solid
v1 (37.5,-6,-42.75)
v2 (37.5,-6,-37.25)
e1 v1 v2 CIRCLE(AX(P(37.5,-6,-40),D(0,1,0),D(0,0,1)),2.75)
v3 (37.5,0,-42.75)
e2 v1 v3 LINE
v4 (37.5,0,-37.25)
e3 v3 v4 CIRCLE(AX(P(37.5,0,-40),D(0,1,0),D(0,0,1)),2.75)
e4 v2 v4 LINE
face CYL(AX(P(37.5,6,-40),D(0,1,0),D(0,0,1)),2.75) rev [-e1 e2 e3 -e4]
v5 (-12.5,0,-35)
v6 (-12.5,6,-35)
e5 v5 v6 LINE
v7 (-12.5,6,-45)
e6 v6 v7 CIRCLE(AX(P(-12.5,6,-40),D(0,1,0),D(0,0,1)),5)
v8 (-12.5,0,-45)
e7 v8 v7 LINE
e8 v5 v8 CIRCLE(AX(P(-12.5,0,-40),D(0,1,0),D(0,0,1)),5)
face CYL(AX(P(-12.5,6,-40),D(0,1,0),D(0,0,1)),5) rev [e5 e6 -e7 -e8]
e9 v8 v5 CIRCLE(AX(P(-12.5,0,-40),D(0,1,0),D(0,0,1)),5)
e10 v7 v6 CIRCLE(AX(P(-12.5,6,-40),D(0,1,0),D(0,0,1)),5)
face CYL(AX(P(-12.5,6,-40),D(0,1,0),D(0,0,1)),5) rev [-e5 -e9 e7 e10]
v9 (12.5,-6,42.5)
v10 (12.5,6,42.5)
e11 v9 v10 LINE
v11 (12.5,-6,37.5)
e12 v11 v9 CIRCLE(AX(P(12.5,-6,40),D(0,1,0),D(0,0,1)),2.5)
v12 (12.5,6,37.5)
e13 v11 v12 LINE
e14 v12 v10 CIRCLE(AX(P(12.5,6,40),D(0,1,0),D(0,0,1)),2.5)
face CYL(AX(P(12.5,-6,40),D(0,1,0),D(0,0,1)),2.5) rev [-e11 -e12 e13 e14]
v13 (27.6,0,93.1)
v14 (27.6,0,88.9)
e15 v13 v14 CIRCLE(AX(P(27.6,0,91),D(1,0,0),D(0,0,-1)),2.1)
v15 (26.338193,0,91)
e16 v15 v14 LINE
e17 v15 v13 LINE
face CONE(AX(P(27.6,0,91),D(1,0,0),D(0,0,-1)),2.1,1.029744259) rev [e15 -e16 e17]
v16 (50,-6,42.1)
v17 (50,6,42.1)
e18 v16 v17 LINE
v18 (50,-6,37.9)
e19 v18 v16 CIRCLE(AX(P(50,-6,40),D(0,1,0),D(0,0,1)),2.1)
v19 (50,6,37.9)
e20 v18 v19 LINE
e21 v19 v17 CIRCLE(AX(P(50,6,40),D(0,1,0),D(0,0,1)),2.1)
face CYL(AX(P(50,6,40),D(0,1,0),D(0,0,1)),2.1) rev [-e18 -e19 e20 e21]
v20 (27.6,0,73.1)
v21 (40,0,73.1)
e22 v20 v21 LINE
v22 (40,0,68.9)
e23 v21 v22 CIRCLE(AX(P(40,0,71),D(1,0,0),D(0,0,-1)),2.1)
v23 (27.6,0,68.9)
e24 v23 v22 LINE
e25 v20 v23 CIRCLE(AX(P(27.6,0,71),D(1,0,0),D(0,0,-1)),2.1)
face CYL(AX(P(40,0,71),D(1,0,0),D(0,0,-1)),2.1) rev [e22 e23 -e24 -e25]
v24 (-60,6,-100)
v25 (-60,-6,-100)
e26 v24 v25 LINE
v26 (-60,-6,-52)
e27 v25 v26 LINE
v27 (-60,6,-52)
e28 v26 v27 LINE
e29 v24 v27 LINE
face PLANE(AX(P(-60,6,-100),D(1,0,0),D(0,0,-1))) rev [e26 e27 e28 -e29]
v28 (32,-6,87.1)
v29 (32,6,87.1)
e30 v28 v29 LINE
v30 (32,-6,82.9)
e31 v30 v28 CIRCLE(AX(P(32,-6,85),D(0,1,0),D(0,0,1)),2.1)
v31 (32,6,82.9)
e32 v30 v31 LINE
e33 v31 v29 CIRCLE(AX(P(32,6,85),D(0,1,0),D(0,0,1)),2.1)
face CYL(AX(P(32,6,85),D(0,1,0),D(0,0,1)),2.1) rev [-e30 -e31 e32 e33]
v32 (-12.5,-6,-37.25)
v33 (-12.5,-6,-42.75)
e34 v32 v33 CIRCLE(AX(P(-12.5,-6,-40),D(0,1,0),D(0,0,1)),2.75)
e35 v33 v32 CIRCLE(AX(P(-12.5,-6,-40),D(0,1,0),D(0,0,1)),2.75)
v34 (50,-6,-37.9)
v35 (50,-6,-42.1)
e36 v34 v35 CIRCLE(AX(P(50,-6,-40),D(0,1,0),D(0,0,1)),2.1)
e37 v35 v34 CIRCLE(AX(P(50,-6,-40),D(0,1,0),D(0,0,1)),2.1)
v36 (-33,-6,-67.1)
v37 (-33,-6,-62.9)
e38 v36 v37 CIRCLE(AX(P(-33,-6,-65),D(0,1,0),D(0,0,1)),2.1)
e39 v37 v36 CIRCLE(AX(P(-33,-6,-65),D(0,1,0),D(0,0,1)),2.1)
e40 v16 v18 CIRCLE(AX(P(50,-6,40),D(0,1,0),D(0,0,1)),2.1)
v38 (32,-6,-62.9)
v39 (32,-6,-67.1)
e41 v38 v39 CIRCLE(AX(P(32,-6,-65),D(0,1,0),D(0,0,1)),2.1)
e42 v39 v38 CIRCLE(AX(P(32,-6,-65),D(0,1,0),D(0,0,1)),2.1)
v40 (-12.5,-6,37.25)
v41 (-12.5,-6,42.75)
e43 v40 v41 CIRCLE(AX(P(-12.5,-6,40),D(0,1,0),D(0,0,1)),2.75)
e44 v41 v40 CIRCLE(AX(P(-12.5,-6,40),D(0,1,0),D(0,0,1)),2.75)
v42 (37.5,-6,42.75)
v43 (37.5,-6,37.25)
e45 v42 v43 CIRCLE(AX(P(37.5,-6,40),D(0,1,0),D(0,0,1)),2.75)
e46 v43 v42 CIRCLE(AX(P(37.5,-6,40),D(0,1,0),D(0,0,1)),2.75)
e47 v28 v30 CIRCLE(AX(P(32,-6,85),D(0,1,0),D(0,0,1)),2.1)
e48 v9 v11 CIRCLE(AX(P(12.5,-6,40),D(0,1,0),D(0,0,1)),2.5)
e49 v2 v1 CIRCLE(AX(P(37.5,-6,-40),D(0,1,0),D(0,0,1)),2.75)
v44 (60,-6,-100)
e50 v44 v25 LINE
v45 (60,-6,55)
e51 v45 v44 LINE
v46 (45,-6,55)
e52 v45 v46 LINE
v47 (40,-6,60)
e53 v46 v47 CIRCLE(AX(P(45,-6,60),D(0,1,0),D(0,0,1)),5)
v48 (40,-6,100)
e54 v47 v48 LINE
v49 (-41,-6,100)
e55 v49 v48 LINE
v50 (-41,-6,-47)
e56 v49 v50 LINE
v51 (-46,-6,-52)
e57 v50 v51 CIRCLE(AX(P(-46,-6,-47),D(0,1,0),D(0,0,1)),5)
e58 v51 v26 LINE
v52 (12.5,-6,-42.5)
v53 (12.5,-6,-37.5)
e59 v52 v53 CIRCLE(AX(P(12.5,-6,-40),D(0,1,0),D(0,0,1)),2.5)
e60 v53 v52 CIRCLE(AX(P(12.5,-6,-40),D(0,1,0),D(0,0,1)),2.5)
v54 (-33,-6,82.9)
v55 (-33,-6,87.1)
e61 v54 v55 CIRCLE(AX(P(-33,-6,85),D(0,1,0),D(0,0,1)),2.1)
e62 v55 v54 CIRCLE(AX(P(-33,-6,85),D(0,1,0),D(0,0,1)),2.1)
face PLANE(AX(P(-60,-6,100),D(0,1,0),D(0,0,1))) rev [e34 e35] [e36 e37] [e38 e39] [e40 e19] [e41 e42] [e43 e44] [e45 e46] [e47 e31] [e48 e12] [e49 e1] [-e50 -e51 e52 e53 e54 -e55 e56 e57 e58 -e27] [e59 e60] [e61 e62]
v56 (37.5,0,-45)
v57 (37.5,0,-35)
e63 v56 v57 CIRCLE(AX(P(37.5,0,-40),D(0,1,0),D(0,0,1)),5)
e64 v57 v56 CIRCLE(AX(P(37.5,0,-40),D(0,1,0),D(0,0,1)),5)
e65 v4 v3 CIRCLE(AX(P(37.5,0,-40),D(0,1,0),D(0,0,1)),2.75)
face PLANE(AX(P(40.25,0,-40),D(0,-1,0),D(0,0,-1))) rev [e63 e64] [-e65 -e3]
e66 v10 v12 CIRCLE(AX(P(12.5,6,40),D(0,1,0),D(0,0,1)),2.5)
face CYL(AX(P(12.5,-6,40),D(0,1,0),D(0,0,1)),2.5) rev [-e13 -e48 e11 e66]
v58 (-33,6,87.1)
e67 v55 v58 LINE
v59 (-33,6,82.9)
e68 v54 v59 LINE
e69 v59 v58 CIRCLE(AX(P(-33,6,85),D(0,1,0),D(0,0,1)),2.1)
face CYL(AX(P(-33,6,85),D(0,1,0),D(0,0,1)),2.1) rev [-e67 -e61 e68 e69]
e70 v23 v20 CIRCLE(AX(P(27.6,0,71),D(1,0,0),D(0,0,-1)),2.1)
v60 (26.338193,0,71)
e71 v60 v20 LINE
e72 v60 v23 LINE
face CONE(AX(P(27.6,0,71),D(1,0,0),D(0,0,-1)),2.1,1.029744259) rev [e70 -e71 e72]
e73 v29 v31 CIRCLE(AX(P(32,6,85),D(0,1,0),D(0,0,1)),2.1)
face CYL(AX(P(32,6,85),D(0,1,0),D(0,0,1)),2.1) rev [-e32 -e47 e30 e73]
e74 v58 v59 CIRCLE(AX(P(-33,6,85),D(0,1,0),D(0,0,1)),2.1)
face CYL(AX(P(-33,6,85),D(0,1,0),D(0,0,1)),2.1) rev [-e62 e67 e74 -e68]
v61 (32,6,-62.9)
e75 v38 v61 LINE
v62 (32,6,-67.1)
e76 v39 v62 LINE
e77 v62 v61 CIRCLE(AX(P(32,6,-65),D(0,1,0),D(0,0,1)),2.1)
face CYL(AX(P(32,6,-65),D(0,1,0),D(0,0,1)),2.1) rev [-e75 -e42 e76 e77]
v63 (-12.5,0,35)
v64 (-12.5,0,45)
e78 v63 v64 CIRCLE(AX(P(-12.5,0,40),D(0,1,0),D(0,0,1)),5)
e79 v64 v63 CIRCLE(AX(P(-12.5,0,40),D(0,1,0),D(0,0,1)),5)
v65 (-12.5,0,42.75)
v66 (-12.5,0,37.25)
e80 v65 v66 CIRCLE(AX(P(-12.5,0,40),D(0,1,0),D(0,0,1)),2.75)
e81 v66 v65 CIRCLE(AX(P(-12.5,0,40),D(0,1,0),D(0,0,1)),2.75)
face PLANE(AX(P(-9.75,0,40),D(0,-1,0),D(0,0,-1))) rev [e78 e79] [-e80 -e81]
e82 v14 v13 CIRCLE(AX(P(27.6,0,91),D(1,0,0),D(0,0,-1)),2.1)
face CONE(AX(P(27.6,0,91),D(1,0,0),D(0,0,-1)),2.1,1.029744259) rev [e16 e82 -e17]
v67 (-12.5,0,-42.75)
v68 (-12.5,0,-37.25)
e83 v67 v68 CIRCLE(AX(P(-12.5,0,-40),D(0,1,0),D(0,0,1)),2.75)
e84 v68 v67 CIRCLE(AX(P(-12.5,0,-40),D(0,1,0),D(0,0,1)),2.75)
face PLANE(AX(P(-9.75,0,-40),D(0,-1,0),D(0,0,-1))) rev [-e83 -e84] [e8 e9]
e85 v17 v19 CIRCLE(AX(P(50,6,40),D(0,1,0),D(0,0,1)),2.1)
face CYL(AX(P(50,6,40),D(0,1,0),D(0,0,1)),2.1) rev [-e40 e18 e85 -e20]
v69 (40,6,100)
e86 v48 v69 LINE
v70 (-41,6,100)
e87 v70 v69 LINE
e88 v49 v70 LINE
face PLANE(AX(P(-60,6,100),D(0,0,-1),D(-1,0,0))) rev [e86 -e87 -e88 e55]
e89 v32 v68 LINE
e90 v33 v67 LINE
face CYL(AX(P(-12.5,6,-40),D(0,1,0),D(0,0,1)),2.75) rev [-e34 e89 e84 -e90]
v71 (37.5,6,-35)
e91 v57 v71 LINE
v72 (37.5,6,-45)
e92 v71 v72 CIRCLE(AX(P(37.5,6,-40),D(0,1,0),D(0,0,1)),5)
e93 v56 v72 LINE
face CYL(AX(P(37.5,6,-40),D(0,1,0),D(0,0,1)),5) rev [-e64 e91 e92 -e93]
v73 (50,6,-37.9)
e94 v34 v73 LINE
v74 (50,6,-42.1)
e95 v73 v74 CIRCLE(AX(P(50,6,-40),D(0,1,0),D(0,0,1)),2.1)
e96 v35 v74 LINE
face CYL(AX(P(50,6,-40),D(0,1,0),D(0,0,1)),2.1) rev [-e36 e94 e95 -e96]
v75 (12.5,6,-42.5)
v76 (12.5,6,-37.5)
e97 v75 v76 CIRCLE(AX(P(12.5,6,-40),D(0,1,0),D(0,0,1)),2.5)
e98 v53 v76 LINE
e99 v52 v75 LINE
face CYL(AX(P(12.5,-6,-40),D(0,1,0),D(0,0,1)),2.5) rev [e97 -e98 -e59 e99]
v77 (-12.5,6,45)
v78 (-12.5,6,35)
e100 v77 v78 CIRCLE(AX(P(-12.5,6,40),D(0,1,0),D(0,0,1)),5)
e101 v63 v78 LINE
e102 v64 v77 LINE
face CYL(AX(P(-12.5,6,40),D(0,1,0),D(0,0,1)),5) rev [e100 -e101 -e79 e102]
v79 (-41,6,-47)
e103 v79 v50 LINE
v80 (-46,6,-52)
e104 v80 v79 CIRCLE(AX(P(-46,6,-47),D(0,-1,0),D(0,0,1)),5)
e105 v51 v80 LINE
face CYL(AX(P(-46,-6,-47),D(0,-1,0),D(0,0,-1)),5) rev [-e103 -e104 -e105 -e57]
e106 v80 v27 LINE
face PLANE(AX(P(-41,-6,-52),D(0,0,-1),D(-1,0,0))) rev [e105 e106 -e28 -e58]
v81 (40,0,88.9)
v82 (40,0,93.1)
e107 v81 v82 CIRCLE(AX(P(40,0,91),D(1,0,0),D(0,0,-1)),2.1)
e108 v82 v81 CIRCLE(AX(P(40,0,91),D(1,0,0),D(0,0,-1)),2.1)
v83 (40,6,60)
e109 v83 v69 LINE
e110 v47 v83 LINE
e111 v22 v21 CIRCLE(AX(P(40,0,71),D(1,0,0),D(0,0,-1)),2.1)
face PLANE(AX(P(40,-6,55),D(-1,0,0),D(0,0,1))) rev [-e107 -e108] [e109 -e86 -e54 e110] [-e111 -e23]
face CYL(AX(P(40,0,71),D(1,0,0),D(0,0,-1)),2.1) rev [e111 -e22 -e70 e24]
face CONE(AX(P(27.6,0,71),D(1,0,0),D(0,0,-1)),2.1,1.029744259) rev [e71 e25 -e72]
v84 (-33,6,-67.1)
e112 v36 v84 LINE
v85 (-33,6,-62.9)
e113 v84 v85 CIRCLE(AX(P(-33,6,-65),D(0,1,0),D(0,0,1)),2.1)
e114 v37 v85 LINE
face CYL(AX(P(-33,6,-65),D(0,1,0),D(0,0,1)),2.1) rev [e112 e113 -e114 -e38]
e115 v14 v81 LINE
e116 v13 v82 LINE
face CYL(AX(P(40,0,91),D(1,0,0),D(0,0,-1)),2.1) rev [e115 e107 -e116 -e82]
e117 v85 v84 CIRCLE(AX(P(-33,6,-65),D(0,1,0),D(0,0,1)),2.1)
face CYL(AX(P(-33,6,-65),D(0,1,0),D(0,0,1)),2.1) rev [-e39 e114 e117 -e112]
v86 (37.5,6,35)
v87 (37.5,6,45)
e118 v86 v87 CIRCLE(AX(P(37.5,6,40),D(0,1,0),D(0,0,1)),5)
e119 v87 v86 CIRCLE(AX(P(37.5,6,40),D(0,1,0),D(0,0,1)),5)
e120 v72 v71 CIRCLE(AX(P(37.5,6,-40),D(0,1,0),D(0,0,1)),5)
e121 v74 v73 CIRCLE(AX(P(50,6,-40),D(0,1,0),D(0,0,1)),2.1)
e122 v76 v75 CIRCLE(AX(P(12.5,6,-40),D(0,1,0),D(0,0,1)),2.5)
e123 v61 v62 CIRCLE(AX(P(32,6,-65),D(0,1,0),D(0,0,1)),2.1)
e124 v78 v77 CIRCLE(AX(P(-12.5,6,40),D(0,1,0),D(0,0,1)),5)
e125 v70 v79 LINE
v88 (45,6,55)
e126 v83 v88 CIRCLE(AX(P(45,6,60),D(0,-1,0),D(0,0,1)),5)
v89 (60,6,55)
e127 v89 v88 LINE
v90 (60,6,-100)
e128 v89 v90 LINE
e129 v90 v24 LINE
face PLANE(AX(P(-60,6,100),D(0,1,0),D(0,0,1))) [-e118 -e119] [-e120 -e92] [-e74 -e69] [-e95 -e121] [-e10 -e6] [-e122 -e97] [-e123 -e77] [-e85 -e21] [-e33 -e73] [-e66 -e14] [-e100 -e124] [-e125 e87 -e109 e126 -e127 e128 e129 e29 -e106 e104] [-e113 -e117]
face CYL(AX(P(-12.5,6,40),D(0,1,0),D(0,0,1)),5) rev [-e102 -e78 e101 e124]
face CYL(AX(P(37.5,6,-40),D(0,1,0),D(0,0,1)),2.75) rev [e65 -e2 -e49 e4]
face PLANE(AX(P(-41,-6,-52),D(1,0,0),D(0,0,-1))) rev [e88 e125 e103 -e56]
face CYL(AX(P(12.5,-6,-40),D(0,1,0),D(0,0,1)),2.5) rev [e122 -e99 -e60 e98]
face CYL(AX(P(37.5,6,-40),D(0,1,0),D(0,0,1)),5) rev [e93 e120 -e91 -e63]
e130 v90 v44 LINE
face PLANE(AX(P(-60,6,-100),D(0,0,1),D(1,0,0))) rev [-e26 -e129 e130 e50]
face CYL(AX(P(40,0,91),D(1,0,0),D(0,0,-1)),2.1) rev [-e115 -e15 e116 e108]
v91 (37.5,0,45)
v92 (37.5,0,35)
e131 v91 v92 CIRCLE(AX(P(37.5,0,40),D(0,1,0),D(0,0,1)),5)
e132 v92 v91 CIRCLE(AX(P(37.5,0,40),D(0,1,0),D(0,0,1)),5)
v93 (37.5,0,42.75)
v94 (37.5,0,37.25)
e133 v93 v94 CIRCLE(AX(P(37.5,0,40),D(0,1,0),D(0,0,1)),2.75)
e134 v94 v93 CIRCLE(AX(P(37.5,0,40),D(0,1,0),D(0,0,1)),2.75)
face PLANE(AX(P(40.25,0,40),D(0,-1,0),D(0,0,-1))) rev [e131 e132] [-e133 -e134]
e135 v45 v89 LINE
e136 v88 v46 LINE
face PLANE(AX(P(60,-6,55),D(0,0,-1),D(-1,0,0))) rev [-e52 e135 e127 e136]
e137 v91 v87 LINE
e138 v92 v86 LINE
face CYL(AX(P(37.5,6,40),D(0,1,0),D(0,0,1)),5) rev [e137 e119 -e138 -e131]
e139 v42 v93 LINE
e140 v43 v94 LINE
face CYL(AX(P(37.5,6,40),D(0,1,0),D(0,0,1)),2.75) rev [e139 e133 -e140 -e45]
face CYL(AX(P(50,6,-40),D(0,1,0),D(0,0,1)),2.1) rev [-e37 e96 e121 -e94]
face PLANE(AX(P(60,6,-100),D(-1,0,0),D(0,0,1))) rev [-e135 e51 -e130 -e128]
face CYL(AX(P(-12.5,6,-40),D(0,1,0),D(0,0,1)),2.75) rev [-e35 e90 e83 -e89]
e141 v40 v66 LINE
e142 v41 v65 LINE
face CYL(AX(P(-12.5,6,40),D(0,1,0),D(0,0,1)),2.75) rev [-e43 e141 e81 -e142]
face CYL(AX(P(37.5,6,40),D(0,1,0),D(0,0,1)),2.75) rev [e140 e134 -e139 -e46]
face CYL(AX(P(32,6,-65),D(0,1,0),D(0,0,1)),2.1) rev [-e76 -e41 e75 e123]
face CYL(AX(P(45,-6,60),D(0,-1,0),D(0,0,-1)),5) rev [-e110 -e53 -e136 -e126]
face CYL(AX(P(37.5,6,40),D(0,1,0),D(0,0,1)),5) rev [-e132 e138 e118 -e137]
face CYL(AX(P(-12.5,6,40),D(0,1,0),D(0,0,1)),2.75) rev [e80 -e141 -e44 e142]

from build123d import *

# Parameters (mm, degrees)
SKETCH1_W                                         = 120
SKETCH1_H                                         = 200
EXTRUDE1_DEPTH                                    = 6
SKETCH3_W                                         = 19
SKETCH3_H                                         = 152
CUT_EXTRUDE1_DEPTH                                = 118.234807118
FILLET1_R                                         = 5
SKETCH4_W                                         = 20
SKETCH4_H                                         = 45
CUT_EXTRUDE2_DEPTH                                = 118.234807118
SKETCH6_R                                         = 2.5
CUT_EXTRUDE3_DEPTH                                = 118.234807118
M5_SOCKET_HEAD_CAP_SCREW_COUNTERBORE1_D           = 5.5
M5_SOCKET_HEAD_CAP_SCREW_COUNTERBORE1_CBORE_D     = 10
M5_SOCKET_HEAD_CAP_SCREW_COUNTERBORE1_CBORE_DEPTH = 6
M5_TAPPED_HOLE1_D                                 = 4.2
FILLET2_R                                         = 5
M5_TAPPED_HOLE2_D                                 = 4.2
M5_TAPPED_HOLE2_DEPTH                             = 12.4
M5_TAPPED_HOLE2_TIP                               = 1.2618073
M5_TAPPED_HOLE3_D                                 = 4.2


with BuildPart() as part:
    # Sketch1 → Extrude1 (new, symmetric)
    with BuildSketch(Plane(origin=(0, 0, 0), x_dir=(1, 0, 0), z_dir=(0, 1, 0))):
        Rectangle(SKETCH1_W, SKETCH1_H)
    extrude(amount=EXTRUDE1_DEPTH, both=True)

    # Sketch3 → Cut-Extrude1 (cut, through all)
    with BuildSketch(Plane(origin=(0, 6, 0), x_dir=(1, 0, 0), z_dir=(0, 1, 0))):
        with Locations((-50.5, -24)):
            Rectangle(SKETCH3_W, SKETCH3_H)
    extrude(amount=-CUT_EXTRUDE1_DEPTH, mode=Mode.SUBTRACT)

    # Fillet1
    fillet1_edges = [part.edges().sort_by_distance(p)[0] for p in [
        (-41, 0, -52),
    ]]
    fillet(fillet1_edges, radius=FILLET1_R)

    # Sketch4 → Cut-Extrude2 (cut, through all)
    with BuildSketch(Plane(origin=(0, 6, 0), x_dir=(1, 0, 0), z_dir=(0, 1, 0))):
        with Locations((50, -77.5)):
            Rectangle(SKETCH4_W, SKETCH4_H)
    extrude(amount=-CUT_EXTRUDE2_DEPTH, mode=Mode.SUBTRACT)

    # Sketch6 → Cut-Extrude3 (cut, through all)
    with BuildSketch(Plane(origin=(0, 6, 0), x_dir=(1, 0, 0), z_dir=(0, 1, 0))):
        with Locations(Location((12.5, 40, 0), (0, 0, 270))):
            Circle(SKETCH6_R)
        with Locations(Location((12.5, -40, 0), (0, 0, 270))):
            Circle(SKETCH6_R)
    extrude(amount=-CUT_EXTRUDE3_DEPTH, mode=Mode.SUBTRACT)

    # M5 Socket Head Cap Screw Counterbore1 (through all)
    with Locations(Plane(origin=(37.5, 6, -40), x_dir=(0, 0, 1), z_dir=(0, 1, 0))):
        with Locations((0, 0), (0, -50), (80, -50), (80, 0)):
            CounterBoreHole(M5_SOCKET_HEAD_CAP_SCREW_COUNTERBORE1_D / 2, M5_SOCKET_HEAD_CAP_SCREW_COUNTERBORE1_CBORE_D / 2, M5_SOCKET_HEAD_CAP_SCREW_COUNTERBORE1_CBORE_DEPTH)

    # M5 Tapped Hole1 (through all)
    with Locations(Plane(origin=(32, 6, 85), x_dir=(0, 0, 1), z_dir=(0, 1, 0))):
        with Locations((0, 0), (0, -65), (-150, 0), (-150, -65)):
            Hole(M5_TAPPED_HOLE1_D / 2)

    # Fillet2
    fillet2_edges = [part.edges().sort_by_distance(p)[0] for p in [
        (40, 0, 55),
    ]]
    fillet(fillet2_edges, radius=FILLET2_R)

    # M5 Tapped Hole2
    with Locations(Plane(origin=(40, 0, 91), x_dir=(0, 0, 1), z_dir=(1, 0, 0))):
        with Locations((0, 0), (-20, 0)):
            Hole(M5_TAPPED_HOLE2_D / 2, depth=M5_TAPPED_HOLE2_DEPTH)
            with Locations((0, 0, -(M5_TAPPED_HOLE2_DEPTH + M5_TAPPED_HOLE2_TIP / 2))):  # 118° drill point
                Cone(0, M5_TAPPED_HOLE2_D / 2, M5_TAPPED_HOLE2_TIP, mode=Mode.SUBTRACT)

    # M5 Tapped Hole3 (through all)
    with Locations(Plane(origin=(50, 6, -40), x_dir=(0, 0, 1), z_dir=(0, 1, 0))):
        with Locations((0, 0), (80, 0)):
            Hole(M5_TAPPED_HOLE3_D / 2)


solid = part.part
